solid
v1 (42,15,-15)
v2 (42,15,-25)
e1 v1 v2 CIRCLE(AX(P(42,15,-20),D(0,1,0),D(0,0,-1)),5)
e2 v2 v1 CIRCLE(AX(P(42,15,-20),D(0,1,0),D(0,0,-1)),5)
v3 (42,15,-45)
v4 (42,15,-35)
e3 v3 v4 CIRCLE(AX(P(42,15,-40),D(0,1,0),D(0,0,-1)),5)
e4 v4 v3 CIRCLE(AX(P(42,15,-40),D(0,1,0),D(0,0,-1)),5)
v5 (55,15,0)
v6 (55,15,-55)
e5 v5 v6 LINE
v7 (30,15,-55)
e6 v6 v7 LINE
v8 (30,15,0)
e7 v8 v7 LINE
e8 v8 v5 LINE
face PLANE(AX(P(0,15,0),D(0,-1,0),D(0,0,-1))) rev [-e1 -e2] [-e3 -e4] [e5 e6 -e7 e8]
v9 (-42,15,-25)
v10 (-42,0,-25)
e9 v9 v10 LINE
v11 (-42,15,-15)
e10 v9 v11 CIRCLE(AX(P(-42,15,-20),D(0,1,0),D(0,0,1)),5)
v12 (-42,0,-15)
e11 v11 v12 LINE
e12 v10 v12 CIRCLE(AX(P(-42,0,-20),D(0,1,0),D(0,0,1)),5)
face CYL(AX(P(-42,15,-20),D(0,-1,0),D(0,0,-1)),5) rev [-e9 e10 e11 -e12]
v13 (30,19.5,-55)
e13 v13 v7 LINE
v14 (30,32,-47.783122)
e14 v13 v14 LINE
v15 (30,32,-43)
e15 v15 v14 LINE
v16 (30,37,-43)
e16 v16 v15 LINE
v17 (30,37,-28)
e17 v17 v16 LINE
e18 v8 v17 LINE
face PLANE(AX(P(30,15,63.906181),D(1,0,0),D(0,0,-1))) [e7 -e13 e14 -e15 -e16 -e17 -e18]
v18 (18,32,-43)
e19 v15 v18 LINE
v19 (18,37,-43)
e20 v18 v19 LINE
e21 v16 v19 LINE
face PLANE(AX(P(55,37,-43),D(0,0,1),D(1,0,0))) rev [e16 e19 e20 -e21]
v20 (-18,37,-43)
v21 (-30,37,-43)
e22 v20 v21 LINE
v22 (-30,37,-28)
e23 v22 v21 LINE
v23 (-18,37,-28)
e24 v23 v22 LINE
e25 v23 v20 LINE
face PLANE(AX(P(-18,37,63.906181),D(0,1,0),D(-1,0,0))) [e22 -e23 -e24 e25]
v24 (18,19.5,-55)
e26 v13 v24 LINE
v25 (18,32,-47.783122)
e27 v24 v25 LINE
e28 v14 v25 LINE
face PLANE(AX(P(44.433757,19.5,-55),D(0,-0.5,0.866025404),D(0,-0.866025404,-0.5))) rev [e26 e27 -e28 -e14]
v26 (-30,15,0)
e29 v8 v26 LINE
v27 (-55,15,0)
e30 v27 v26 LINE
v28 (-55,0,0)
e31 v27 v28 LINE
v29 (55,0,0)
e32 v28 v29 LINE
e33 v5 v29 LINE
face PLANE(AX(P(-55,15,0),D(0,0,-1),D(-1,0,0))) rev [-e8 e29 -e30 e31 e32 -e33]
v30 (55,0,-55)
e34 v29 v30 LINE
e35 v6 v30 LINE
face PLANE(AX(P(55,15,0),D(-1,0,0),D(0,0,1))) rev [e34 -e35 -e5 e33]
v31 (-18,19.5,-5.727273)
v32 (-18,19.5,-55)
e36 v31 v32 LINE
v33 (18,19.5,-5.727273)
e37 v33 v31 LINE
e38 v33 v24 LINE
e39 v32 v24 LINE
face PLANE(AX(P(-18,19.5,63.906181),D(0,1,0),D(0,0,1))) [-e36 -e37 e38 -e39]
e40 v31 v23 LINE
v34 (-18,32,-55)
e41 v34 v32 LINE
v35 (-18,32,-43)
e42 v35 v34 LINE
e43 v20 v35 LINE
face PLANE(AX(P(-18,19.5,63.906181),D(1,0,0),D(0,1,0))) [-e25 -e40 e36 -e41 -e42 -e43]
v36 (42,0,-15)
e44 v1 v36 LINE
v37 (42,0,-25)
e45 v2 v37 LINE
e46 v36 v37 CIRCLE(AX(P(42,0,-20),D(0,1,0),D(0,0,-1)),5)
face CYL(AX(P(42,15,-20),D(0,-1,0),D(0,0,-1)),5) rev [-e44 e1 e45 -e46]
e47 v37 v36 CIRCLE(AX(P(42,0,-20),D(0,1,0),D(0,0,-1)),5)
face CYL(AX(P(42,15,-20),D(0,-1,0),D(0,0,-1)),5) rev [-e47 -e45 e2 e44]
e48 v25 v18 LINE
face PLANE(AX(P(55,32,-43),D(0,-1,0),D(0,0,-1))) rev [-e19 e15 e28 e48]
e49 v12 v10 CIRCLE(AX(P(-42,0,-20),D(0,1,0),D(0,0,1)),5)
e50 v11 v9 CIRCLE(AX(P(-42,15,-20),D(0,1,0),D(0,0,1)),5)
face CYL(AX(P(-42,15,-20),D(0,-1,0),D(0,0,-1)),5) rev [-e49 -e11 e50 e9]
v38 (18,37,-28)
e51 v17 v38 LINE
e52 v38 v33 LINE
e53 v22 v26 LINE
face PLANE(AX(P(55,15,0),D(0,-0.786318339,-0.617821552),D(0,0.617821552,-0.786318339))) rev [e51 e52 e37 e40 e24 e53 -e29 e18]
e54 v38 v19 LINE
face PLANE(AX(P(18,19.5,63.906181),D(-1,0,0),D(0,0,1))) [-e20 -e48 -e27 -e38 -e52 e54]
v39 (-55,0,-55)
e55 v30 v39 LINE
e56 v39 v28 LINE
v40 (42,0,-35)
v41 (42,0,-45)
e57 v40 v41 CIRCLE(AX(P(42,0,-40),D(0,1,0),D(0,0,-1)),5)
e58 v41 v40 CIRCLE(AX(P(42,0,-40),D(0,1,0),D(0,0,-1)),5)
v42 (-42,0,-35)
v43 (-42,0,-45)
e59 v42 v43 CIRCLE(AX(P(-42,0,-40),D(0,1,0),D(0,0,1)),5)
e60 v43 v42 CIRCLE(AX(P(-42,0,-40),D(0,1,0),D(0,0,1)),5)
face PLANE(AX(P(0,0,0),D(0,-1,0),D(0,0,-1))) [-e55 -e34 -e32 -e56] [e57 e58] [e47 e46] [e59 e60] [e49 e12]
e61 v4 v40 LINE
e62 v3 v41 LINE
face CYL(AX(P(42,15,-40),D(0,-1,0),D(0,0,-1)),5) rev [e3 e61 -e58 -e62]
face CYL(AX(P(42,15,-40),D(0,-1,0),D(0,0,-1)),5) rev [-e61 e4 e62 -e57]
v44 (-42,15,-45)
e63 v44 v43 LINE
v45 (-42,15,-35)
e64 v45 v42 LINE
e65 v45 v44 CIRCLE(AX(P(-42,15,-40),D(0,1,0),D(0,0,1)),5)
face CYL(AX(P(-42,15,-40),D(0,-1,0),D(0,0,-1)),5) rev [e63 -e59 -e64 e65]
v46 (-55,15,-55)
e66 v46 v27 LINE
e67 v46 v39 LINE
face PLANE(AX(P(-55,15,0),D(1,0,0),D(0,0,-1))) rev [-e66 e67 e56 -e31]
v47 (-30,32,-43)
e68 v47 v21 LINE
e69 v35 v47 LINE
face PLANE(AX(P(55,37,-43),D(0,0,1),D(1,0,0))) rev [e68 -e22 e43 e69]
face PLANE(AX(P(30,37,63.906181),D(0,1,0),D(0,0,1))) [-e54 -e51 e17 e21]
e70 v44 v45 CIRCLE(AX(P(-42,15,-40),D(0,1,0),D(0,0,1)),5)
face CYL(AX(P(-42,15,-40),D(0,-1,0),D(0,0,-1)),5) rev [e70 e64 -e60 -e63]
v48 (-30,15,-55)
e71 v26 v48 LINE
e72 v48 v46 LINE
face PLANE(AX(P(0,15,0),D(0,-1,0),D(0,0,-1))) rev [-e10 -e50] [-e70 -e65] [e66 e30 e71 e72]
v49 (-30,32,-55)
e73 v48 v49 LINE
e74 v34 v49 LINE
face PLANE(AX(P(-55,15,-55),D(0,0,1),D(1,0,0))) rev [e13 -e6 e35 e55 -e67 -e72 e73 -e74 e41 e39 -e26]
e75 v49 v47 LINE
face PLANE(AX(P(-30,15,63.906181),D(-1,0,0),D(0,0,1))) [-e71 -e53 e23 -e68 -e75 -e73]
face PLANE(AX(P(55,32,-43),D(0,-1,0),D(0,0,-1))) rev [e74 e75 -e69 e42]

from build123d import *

# Parameters (mm, degrees)
BASE_PLATE_SKETCH_W    = 110
BASE_PLATE_SKETCH_H    = 55
BASE_PLATE_SKETCH_R    = 5
BASE_PLATE_DEPTH       = 15
V_BLOCK_UPRIGHTS_DEPTH = 55
UPRIGHT_NOTCH_SKETCH_W = 12
UPRIGHT_NOTCH_SKETCH_H = 5
UPRIGHT_NOTCH_DEPTH    = 108.791465339
ANGLED_CUT_30DEG_DEPTH = 12


with BuildPart() as part:
    # Base Plate Sketch → Base Plate (new body)
    with BuildSketch(Plane(origin=(0, 0, 0), x_dir=(1, 0, 0), z_dir=(0, 1, 0))):
        with Locations((0, 27.5)):
            Rectangle(BASE_PLATE_SKETCH_W, BASE_PLATE_SKETCH_H)
        with Locations(Location((-42, 40, 0), (0, 0, 270))):
            Circle(BASE_PLATE_SKETCH_R, mode=Mode.SUBTRACT)
        with Locations(Location((-42, 20, 0), (0, 0, 270))):
            Circle(BASE_PLATE_SKETCH_R, mode=Mode.SUBTRACT)
        with Locations(Location((42, 20, 0), (0, 0, 90))):
            Circle(BASE_PLATE_SKETCH_R, mode=Mode.SUBTRACT)
        with Locations(Location((42, 40, 0), (0, 0, 90))):
            Circle(BASE_PLATE_SKETCH_R, mode=Mode.SUBTRACT)
    extrude(amount=BASE_PLATE_DEPTH)

    # V-Block Uprights Sketch → V-Block Uprights (add)
    with BuildSketch(Plane(origin=(0, 0, -55), x_dir=(-1, 0, 0), z_dir=(0, 0, -1))):
        Polygon((-30, 15), (-18, 15), (18, 15), (30, 15), (30, 37), (18, 37), (18, 19.5), (-18, 19.5), (-18, 37), (-30, 37), align=None)
    extrude(amount=-V_BLOCK_UPRIGHTS_DEPTH)

    # Upright Notch Sketch → Upright Notch (cut, through all)
    with BuildSketch(Plane.ZY.offset(30)):
        Polygon((0, 15), (-28, 37), (0, 37), align=None)
        with Locations((-49, 34.5)):
            Rectangle(UPRIGHT_NOTCH_SKETCH_W, UPRIGHT_NOTCH_SKETCH_H)
    extrude(amount=-UPRIGHT_NOTCH_DEPTH, mode=Mode.SUBTRACT)

    # Angled Cut 30deg Sketch → Angled Cut 30deg (cut)
    with BuildSketch(Plane.ZY.offset(-18)):
        Polygon((-55, 19.5), (-47.783121635, 32), (-55, 32), align=None)
    extrude(amount=-ANGLED_CUT_30DEG_DEPTH, mode=Mode.SUBTRACT)


solid = part.part
